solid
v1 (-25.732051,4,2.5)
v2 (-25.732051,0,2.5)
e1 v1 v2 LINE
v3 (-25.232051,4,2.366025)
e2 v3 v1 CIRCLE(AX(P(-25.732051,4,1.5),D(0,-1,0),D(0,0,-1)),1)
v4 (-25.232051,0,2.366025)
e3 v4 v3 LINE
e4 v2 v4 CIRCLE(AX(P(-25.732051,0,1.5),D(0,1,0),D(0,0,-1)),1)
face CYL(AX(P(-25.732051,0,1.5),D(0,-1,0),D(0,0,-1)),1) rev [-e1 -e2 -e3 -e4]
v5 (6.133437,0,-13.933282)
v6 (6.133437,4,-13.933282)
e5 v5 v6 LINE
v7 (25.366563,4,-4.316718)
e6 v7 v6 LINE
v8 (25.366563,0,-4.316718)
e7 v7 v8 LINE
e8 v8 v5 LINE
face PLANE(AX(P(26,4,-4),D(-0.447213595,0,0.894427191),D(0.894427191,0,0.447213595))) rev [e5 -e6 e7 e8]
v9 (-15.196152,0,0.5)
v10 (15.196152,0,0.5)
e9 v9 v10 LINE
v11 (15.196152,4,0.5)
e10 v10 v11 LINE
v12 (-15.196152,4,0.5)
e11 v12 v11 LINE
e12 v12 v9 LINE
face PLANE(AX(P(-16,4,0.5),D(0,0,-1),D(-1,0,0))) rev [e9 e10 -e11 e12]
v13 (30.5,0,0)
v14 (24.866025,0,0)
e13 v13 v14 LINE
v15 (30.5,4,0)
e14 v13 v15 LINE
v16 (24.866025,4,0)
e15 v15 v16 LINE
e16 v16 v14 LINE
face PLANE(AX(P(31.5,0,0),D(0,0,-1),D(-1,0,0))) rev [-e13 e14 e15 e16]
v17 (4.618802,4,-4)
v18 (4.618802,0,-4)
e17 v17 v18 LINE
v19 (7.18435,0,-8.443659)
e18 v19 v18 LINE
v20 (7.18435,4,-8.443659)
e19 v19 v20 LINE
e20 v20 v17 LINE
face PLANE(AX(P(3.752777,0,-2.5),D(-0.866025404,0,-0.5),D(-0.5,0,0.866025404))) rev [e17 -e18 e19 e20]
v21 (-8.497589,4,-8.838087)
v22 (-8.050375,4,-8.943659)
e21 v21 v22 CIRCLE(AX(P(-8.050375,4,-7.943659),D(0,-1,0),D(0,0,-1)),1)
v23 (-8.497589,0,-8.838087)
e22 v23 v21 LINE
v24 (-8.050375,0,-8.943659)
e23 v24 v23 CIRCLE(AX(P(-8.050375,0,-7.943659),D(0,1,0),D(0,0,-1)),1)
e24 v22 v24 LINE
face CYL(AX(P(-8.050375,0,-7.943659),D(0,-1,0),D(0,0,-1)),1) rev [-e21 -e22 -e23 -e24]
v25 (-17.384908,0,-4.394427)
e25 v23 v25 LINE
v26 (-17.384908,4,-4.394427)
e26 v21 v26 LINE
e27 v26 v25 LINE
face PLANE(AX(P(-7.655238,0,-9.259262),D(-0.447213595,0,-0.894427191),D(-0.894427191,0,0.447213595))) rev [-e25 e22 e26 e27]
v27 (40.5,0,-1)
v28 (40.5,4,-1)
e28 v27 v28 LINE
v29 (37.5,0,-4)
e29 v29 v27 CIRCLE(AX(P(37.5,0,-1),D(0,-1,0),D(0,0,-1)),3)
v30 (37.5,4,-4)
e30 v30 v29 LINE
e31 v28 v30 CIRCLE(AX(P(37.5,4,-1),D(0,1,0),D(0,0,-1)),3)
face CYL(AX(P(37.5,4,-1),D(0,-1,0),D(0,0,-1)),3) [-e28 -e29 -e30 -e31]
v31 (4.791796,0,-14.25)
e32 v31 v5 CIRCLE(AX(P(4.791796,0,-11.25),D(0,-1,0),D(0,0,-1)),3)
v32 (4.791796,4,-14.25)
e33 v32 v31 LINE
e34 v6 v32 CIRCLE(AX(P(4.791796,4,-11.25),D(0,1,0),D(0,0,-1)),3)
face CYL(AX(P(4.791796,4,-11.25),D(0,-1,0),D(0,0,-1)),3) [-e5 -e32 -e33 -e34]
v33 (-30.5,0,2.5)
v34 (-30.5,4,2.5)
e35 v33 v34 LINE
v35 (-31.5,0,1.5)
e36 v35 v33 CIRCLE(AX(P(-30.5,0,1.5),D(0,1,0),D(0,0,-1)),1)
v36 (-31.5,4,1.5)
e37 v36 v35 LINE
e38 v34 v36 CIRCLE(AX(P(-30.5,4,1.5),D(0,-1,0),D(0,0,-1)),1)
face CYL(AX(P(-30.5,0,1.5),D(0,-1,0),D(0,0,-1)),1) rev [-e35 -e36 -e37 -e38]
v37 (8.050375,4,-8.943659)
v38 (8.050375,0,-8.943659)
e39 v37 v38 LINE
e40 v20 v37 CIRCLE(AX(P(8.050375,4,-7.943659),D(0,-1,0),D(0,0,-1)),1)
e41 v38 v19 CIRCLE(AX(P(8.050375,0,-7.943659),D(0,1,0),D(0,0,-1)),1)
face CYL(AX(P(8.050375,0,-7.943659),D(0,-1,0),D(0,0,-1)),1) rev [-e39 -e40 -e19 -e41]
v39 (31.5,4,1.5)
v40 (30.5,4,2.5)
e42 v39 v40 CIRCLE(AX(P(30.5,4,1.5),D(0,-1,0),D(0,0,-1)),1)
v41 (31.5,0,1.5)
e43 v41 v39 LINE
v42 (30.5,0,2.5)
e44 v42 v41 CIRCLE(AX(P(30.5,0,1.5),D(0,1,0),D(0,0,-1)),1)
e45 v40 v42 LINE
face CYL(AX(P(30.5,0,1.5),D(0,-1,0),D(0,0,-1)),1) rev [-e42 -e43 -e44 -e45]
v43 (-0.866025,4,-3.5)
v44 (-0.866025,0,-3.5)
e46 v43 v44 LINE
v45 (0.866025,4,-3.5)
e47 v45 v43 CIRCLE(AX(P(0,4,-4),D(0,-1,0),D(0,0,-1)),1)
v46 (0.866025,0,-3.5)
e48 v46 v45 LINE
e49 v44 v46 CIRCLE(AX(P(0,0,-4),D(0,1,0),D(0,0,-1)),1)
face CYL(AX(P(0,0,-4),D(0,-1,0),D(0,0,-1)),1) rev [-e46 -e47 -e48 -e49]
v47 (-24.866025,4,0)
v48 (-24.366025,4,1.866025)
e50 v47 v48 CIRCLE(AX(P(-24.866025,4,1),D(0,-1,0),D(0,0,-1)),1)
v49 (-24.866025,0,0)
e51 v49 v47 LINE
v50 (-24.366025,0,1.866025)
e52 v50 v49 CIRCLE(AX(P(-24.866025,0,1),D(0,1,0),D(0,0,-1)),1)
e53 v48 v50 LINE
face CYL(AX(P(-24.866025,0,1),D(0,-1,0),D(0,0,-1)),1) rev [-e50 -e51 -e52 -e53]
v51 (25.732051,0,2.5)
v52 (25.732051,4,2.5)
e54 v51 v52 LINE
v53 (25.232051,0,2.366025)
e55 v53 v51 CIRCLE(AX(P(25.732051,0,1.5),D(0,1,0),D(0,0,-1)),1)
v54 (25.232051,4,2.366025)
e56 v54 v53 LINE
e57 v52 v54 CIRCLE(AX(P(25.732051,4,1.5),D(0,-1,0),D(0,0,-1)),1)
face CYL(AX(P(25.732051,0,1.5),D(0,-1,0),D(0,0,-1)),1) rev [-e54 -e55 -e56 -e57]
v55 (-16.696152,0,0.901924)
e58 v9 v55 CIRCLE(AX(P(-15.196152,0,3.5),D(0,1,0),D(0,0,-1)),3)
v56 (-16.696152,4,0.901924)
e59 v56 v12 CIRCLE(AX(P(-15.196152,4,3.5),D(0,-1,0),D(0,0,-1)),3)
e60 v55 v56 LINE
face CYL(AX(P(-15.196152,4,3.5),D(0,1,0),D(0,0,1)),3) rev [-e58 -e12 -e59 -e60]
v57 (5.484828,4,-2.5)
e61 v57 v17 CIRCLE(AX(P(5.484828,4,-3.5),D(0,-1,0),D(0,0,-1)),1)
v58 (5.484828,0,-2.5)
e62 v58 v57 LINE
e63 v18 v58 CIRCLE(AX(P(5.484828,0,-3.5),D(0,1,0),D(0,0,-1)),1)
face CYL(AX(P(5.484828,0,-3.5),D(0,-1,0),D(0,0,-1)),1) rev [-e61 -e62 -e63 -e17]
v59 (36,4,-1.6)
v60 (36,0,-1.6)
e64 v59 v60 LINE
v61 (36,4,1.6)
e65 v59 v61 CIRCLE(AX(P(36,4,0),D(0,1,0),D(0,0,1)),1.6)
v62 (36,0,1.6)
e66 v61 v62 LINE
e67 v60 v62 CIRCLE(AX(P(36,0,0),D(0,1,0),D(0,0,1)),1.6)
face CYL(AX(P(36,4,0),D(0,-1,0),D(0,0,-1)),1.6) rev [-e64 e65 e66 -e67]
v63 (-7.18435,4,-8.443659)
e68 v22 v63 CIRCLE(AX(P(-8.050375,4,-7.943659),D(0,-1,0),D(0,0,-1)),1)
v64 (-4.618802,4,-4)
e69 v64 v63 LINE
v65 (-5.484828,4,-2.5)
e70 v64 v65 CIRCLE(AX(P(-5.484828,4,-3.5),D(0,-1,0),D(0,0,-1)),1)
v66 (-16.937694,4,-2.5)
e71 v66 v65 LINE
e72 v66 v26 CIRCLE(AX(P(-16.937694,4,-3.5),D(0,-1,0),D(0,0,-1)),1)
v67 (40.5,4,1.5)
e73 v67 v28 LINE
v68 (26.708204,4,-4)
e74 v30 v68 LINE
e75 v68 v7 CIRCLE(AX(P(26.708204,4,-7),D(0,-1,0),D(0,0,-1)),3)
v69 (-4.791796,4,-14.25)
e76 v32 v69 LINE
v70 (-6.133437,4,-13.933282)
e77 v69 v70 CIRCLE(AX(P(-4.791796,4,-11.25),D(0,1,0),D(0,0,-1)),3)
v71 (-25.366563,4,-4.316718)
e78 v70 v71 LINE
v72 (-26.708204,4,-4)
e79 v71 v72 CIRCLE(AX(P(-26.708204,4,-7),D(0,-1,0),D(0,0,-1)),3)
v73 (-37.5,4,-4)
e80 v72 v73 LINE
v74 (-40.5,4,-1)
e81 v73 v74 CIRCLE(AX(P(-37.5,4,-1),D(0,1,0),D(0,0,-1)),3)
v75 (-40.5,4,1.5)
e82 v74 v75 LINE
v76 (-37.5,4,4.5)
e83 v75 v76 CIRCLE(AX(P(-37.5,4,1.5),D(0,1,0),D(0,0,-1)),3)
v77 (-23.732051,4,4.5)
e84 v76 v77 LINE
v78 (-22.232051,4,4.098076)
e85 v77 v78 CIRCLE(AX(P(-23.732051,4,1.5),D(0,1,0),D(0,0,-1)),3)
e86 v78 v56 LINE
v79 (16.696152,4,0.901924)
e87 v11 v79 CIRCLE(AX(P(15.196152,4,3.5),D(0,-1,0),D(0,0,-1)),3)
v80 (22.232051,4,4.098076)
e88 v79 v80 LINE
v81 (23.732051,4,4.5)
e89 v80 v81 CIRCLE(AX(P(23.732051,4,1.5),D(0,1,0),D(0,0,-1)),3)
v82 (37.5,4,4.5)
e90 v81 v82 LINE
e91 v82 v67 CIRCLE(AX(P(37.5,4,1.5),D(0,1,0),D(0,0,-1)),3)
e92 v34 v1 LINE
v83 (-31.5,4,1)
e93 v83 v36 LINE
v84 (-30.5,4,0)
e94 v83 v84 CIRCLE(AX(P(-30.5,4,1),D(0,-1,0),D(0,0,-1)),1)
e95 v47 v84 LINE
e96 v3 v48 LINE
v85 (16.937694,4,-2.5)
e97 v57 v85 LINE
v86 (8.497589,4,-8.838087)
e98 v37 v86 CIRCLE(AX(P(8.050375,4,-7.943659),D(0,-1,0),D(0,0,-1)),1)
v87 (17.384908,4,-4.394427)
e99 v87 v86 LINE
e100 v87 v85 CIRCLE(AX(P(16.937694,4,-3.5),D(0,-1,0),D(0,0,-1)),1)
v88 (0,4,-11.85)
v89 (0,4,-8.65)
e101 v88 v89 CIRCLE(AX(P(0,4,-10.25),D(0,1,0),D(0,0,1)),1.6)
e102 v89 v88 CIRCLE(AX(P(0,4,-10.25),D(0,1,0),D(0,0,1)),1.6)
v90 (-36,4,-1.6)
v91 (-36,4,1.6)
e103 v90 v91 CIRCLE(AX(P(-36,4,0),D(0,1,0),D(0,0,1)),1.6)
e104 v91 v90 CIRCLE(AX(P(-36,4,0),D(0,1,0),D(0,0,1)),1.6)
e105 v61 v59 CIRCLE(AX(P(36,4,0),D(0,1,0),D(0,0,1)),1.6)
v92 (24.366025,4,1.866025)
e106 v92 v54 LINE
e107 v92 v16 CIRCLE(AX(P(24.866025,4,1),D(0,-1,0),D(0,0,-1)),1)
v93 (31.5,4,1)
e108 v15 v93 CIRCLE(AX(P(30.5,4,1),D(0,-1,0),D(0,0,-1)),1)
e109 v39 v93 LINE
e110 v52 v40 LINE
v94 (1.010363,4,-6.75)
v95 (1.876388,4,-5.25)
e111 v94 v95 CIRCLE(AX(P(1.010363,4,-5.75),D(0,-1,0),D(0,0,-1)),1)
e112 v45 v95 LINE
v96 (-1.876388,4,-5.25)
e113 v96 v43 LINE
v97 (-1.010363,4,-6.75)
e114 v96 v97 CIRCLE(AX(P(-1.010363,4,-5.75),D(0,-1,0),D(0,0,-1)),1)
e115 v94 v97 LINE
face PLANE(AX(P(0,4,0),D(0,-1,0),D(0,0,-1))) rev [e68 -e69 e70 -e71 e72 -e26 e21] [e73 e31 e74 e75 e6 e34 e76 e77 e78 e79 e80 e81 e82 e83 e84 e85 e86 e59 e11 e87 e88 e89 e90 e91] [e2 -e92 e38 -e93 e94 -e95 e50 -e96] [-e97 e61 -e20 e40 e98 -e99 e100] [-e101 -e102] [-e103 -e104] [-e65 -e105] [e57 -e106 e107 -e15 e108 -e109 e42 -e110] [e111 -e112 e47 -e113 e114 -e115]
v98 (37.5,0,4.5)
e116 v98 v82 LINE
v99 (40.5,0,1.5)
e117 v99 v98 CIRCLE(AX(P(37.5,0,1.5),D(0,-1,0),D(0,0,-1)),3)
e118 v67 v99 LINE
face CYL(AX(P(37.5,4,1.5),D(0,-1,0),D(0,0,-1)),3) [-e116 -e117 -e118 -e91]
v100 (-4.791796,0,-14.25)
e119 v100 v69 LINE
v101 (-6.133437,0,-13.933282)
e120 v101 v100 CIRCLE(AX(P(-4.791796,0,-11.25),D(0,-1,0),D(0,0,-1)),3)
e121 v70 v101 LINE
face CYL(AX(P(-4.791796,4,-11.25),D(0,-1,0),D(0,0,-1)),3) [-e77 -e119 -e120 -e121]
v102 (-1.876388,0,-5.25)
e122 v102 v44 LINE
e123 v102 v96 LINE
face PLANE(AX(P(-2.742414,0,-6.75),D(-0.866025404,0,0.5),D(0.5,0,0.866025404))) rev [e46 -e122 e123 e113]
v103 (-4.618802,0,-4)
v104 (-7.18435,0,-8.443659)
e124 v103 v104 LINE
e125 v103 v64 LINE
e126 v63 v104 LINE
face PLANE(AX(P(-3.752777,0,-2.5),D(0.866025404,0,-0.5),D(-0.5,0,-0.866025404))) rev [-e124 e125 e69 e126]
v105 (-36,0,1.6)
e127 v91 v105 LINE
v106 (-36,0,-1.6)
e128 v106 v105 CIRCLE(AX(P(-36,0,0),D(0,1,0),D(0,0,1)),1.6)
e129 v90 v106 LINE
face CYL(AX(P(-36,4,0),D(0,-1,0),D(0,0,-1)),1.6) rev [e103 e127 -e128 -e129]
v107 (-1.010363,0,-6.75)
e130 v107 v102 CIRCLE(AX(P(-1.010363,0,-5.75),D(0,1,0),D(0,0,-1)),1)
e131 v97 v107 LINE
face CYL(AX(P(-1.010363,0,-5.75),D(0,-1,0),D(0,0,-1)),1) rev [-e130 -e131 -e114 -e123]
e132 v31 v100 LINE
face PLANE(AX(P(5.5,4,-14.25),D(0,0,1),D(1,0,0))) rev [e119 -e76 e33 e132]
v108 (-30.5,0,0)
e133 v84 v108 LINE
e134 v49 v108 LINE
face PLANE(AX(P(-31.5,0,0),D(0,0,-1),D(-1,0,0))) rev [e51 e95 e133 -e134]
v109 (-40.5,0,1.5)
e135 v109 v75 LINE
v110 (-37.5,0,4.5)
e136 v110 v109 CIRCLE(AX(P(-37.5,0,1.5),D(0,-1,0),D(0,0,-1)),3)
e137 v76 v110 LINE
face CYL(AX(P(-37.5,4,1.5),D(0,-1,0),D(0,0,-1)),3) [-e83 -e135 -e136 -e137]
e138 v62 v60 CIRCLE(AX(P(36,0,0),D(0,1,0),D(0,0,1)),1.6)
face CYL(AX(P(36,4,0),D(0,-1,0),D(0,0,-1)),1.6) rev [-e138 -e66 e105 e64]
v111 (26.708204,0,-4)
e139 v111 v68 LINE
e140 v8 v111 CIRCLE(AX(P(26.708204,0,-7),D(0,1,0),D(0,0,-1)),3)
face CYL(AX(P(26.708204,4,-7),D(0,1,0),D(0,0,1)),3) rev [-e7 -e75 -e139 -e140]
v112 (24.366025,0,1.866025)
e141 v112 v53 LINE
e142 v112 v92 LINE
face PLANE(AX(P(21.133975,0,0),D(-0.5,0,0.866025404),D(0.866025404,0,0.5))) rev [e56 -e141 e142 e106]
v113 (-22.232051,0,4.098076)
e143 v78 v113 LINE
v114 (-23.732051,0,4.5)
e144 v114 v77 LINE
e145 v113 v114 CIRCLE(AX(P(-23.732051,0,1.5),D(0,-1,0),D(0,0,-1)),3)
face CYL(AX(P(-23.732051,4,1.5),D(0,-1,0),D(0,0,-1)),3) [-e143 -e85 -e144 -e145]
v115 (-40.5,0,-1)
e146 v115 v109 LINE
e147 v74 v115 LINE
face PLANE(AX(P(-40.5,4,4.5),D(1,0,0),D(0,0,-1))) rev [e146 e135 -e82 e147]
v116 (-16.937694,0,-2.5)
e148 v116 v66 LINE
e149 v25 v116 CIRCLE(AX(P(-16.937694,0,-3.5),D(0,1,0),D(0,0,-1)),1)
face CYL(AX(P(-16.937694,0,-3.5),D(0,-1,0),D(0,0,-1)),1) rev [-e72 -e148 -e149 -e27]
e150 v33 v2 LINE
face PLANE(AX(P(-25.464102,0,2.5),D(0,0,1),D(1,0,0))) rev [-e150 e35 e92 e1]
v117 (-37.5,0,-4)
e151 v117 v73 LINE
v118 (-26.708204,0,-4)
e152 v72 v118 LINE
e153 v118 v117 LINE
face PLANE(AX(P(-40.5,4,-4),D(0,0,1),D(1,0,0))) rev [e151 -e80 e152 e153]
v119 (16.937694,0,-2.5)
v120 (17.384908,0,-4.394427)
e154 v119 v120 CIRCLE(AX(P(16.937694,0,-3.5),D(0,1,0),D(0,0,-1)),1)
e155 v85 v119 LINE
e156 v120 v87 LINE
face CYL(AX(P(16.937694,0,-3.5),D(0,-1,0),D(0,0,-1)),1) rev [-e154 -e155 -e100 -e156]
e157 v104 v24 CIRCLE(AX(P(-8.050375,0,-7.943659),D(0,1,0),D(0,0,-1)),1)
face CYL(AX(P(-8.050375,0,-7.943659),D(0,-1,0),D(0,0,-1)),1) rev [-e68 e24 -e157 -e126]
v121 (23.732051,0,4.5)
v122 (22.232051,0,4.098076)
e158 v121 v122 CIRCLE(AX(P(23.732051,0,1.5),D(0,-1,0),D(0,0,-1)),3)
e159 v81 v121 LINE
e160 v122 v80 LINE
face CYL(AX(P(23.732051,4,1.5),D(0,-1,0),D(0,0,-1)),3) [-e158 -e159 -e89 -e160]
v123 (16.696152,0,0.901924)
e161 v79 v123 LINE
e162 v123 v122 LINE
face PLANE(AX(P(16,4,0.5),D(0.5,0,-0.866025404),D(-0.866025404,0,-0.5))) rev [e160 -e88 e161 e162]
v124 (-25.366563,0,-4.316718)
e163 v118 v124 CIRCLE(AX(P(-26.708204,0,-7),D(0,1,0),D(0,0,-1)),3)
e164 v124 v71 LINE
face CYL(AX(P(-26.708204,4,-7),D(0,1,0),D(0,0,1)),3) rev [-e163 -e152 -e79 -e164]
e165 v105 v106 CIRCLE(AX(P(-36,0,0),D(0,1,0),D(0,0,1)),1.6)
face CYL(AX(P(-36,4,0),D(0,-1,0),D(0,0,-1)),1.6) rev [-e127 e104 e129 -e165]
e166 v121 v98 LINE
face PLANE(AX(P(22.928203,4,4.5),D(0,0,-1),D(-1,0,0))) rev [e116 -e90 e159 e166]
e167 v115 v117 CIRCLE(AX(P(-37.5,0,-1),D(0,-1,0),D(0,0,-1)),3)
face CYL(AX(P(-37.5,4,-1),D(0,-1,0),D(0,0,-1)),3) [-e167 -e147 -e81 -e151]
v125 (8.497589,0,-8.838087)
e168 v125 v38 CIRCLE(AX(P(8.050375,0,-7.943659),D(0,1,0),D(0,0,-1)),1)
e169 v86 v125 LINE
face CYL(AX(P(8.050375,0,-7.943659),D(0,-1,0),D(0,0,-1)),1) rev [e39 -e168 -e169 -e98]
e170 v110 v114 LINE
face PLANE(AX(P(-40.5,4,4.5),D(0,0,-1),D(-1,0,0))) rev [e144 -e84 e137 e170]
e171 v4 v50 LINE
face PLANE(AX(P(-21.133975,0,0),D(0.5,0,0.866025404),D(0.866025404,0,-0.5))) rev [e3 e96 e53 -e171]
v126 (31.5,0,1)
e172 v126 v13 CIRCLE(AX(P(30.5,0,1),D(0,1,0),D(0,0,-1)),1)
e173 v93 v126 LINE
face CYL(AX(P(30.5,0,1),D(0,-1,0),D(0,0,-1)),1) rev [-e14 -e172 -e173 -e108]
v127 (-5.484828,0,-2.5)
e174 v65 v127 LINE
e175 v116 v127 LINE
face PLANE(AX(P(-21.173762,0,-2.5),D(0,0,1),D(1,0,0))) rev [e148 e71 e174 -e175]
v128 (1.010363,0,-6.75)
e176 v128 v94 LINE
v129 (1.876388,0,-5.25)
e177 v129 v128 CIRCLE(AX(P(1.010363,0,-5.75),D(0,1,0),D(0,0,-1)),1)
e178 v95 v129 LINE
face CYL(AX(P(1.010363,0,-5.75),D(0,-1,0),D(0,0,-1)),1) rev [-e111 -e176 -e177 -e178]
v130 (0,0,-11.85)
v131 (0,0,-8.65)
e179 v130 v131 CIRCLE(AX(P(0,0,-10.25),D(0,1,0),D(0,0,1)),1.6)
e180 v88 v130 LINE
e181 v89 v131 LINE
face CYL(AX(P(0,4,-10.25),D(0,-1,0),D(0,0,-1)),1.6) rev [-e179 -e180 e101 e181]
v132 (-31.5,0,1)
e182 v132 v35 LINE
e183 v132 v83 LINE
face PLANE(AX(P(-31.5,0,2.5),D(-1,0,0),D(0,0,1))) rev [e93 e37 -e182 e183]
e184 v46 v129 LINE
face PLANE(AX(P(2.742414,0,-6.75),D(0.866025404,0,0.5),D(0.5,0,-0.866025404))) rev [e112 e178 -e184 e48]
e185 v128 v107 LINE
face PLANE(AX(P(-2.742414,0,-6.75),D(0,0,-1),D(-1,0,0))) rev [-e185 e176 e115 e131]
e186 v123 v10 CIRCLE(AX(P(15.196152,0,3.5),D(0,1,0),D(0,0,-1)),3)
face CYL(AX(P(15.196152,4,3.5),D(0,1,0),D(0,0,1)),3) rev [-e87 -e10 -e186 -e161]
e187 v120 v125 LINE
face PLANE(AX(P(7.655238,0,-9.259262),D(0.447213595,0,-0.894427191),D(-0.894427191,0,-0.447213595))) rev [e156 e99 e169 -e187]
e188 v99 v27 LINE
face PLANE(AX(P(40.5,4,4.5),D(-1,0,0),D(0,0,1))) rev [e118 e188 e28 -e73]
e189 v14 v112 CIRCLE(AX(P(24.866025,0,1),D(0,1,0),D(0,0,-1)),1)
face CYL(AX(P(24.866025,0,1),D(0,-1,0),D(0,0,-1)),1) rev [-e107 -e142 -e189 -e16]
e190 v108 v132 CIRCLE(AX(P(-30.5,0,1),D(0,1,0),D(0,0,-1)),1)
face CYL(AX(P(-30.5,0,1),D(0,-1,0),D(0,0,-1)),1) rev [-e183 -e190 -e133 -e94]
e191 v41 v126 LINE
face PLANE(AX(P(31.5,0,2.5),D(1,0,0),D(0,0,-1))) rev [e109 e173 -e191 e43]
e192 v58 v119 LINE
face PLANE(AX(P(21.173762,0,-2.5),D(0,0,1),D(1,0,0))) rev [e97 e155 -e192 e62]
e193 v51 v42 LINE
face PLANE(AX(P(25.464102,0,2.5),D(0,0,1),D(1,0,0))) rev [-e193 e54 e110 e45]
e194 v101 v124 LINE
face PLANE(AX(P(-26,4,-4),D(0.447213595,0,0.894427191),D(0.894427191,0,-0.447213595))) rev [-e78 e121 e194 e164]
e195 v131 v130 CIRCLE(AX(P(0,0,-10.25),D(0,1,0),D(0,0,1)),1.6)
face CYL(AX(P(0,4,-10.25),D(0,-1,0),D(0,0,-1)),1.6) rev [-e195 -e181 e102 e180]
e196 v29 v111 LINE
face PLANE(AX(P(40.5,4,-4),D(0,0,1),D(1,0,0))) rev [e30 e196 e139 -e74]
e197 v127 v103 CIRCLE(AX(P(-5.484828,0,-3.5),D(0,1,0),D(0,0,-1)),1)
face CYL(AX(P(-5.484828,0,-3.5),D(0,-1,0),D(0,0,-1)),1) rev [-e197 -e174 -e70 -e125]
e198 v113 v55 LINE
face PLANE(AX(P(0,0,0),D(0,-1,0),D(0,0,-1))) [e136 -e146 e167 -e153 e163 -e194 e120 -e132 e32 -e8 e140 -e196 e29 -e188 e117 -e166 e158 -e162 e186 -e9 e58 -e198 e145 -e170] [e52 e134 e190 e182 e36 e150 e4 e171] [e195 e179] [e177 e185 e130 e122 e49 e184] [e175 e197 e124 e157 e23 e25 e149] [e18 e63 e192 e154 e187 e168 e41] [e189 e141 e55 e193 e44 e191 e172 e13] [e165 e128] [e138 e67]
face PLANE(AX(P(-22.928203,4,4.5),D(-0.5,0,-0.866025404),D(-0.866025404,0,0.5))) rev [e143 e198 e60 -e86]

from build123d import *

# Parameters (mm, degrees)
SKETCH1_R              = 1.6
BOSS_EXTRUDE1_DEPTH    = 4
CUT_EXTRUDE1_DEPTH     = 44.119746057
R1_CUTOUT_FILLET_R     = 1
R3_OUTER_EDGE_FILLET_R = 3


with BuildPart() as part:
    # Sketch1 → Boss-Extrude1 (new body)
    with BuildSketch(Plane(origin=(0, 0, 0), x_dir=(1, 0, 0), z_dir=(0, 1, 0))):
        Polygon((-40.5, -4.5), (-22.92820323, -4.5), (-16, -0.5), (16, -0.5), (22.92820323, -4.5), (40.5, -4.5), (40.5, 4), (26, 4), (5.5, 14.25), (-5.5, 14.25), (-26, 4), (-40.5, 4), align=None)
        with Locations(Location((-36, 0, 0), (0, 0, 270))):
            Circle(SKETCH1_R, mode=Mode.SUBTRACT)
        with Locations(Location((36, 0, 0), (0, 0, 270))):
            Circle(SKETCH1_R, mode=Mode.SUBTRACT)
        with Locations(Location((0, 10.25, 0), (0, 0, 270))):
            Circle(SKETCH1_R, mode=Mode.SUBTRACT)
    extrude(amount=BOSS_EXTRUDE1_DEPTH)

    # Sketch2 → Cut-Extrude1 (cut, through all)
    with BuildSketch(Plane(origin=(0, 4, 0), x_dir=(1, 0, 0), z_dir=(0, 1, 0))):
        Polygon((-7.655238394, 9.259261842), (-21.173762079, 2.5), (-3.75277675, 2.5), align=None)
        Polygon((-2.742413779, 6.75), (0, 2), (2.742413779, 6.75), align=None)
        Polygon((21.173762079, 2.5), (3.75277675, 2.5), (7.655238394, 9.259261842), align=None)
        Polygon((-31.5, 0), (-21.133974596, 0), (-25.464101615, -2.5), (-31.5, -2.5), align=None)
        Polygon((25.464101615, -2.5), (31.5, -2.5), (31.5, 0), (21.133974596, 0), align=None)
    extrude(amount=-CUT_EXTRUDE1_DEPTH, mode=Mode.SUBTRACT)

    # R1 cutout fillet
    r1_cutout_fillet_edges = [part.edges().sort_by_distance(p)[0] for p in [
        (-25.464101615, 2, 2.5),
        (-31.5, 2, 2.5),
        (-31.5, 2, 0),
        (-21.133974596, 2, 0),
        (25.464101615, 2, 2.5),
        (21.133974596, 2, 0),
        (31.5, 2, 0),
        (31.5, 2, 2.5),
        (7.655238394, 2, -9.259261842),
        (21.173762079, 2, -2.5),
        (3.75277675, 2, -2.5),
        (-2.742413779, 2, -6.75),
        (2.742413779, 2, -6.75),
        (0, 2, -2),
        (-7.655238394, 2, -9.259261842),
        (-3.75277675, 2, -2.5),
        (-21.173762079, 2, -2.5),
    ]]
    fillet(r1_cutout_fillet_edges, radius=R1_CUTOUT_FILLET_R)

    # R3 outer edge fillet
    r3_outer_edge_fillet_edges = [part.edges().sort_by_distance(p)[0] for p in [
        (40.5, 2, -4),
        (40.5, 2, 4.5),
        (22.92820323, 2, 4.5),
        (16, 2, 0.5),
        (-16, 2, 0.5),
        (-22.92820323, 2, 4.5),
        (-40.5, 2, 4.5),
        (-40.5, 2, -4),
        (-26, 2, -4),
        (-5.5, 2, -14.25),
        (5.5, 2, -14.25),
        (26, 2, -4),
    ]]
    fillet(r3_outer_edge_fillet_edges, radius=R3_OUTER_EDGE_FILLET_R)


solid = part.part
